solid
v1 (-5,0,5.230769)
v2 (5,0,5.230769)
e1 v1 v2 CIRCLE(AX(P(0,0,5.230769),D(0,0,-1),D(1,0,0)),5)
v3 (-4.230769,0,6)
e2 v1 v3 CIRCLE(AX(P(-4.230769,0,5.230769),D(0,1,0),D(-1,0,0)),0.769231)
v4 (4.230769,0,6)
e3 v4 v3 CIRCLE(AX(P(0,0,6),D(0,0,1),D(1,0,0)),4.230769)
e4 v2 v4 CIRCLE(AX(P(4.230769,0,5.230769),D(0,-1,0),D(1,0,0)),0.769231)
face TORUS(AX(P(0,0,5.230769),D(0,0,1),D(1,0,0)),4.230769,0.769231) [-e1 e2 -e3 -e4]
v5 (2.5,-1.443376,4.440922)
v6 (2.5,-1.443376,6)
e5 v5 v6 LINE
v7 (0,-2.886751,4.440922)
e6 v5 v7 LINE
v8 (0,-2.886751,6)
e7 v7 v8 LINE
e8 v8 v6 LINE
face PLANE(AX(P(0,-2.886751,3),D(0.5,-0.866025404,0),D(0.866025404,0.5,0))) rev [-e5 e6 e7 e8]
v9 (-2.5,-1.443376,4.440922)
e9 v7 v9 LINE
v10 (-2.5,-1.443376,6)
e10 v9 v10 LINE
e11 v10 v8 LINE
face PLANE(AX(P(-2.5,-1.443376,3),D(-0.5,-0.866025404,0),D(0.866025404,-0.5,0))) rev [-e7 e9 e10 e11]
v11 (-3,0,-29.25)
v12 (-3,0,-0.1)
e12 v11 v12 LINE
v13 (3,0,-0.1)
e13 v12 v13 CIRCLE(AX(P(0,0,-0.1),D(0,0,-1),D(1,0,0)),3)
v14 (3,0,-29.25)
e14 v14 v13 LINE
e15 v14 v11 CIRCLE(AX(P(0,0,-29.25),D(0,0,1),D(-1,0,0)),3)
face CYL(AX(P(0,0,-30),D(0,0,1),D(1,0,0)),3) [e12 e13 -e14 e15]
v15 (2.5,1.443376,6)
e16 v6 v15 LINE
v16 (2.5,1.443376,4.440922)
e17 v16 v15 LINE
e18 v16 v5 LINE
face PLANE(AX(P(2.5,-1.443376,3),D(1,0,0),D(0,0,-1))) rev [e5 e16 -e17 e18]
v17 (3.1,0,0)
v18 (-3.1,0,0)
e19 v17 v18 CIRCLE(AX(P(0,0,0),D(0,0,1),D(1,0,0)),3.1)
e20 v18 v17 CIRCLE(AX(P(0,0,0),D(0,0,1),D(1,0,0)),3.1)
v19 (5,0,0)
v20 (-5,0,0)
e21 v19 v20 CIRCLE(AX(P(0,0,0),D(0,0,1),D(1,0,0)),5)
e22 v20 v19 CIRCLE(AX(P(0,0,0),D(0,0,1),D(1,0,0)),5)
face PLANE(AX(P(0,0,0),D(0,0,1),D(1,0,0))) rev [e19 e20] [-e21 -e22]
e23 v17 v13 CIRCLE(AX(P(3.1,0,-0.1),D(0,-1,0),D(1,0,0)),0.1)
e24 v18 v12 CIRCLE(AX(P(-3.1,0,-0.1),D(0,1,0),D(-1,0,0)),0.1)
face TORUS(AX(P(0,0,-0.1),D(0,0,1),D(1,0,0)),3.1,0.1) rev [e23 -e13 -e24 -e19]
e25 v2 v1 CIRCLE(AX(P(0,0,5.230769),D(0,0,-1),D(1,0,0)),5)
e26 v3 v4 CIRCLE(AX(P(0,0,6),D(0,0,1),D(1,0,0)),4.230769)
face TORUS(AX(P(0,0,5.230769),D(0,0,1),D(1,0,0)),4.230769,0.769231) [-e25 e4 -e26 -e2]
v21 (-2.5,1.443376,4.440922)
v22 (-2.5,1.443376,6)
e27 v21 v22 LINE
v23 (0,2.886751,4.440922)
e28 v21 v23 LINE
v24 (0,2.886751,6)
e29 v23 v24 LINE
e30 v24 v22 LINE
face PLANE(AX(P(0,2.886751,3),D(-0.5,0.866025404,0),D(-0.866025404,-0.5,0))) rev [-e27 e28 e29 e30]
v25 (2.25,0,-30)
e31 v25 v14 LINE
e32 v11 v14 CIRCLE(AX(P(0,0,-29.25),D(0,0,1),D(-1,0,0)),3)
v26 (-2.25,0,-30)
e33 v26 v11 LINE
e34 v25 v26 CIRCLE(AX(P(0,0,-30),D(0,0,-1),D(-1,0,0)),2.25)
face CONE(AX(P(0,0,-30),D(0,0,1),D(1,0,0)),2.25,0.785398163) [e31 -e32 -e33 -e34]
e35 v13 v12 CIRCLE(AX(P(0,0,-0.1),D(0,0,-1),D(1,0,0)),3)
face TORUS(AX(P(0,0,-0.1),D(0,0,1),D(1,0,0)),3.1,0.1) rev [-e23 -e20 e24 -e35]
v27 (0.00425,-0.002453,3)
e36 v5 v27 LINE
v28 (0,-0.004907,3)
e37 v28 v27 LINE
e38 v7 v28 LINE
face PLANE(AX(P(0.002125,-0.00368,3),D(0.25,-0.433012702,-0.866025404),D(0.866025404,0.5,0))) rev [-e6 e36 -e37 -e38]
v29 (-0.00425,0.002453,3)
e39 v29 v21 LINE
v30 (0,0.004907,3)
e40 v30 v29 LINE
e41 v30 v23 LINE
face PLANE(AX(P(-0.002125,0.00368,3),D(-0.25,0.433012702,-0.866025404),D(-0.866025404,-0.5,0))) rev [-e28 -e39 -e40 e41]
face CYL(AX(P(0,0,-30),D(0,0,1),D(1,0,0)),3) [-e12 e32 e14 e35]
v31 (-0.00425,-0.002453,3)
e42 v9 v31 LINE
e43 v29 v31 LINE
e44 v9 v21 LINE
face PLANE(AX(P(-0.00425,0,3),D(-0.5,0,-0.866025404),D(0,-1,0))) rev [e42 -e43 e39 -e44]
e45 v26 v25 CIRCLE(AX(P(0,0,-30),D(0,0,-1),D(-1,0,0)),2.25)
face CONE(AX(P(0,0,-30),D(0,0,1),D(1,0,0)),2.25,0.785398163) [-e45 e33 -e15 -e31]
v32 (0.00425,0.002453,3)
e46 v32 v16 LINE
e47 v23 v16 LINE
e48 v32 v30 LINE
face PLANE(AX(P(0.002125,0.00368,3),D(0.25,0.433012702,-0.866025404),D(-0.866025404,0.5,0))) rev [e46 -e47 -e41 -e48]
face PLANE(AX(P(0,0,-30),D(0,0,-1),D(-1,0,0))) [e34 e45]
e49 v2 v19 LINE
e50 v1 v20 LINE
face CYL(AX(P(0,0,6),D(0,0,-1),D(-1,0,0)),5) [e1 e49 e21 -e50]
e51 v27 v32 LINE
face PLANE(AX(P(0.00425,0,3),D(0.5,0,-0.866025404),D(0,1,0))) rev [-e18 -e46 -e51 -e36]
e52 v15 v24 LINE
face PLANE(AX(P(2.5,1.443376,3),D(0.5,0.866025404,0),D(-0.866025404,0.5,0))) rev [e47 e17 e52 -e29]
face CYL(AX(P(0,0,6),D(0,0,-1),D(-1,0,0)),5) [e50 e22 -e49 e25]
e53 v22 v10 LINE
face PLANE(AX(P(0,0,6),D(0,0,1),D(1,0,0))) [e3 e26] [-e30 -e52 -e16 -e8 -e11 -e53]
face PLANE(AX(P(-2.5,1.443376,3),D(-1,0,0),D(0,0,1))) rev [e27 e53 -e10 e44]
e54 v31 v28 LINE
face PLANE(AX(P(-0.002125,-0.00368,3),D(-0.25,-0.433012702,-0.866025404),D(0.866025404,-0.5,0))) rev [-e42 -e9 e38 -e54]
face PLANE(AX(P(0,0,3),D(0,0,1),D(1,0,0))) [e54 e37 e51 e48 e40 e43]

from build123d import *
from OCP.BRepFilletAPI import BRepFilletAPI_MakeChamfer

# Parameters (mm, degrees)
SKETCH1_R           = 5
BOSS_EXTRUDE1_DEPTH = 6
CUT_EXTRUDE1_DEPTH  = 3
SKETCH3_R           = 3
BOSS_EXTRUDE2_DEPTH = 30
CHAMFER1_SIZE       = 0.75
FILLET1_R           = 0.769230769
CHAMFER2_SIZE       = 1.44092219
CHAMFER2_SIZE2      = 2.495750443
FILLET2_R           = 0.1


with BuildPart() as part:
    # Sketch1 → Boss-Extrude1 (new body)
    with BuildSketch(Plane.XY):
        Circle(SKETCH1_R)
    extrude(amount=BOSS_EXTRUDE1_DEPTH)

    # Sketch2 → Cut-Extrude1 (cut)
    with BuildSketch(Plane.XY.offset(6)):
        Polygon((2.5, 1.443375673), (0, 2.886751346), (-2.5, 1.443375673), (-2.5, -1.443375673), (0, -2.886751346), (2.5, -1.443375673), align=None)
    extrude(amount=-CUT_EXTRUDE1_DEPTH, mode=Mode.SUBTRACT)

    # Sketch3 → Boss-Extrude2 (add)
    with BuildSketch(Plane(origin=(0, 0, 0), x_dir=(-1, 0, 0), z_dir=(0, 0, -1))):
        with Locations(Location((0, 0, 0), (0, 0, 180))):
            Circle(SKETCH3_R)
    extrude(amount=BOSS_EXTRUDE2_DEPTH)

    # Chamfer1
    chamfer1_edges = [part.edges().sort_by_distance(p)[0] for p in [
        (-3, 0, -30),
    ]]
    chamfer(chamfer1_edges, length=CHAMFER1_SIZE)

    # Fillet1
    fillet1_edges = [part.edges().sort_by_distance(p)[0] for p in [
        (-5, 0, 6),
    ]]
    fillet(fillet1_edges, radius=FILLET1_R)

    # Chamfer2: one chamfer whose edges measure the first distance from different faces: ONE call of the kernel's chamfer builder (chamfer() names one face for all edges)
    chamfer2_edges_1 = [part.edges().sort_by_distance(p)[0] for p in [
        (-1.25, 2.165063509, 3),
    ]]
    chamfer2_side_1 = [part.faces().sort_by_distance(p)[0] for p in [
        (-1.25, 2.165063509, 4.5),
    ]]
    chamfer2_edges_2 = [part.edges().sort_by_distance(p)[0] for p in [
        (1.25, 2.165063509, 3),
    ]]
    chamfer2_side_2 = [part.faces().sort_by_distance(p)[0] for p in [
        (1.25, 2.165063509, 4.5),
    ]]
    chamfer2_edges_3 = [part.edges().sort_by_distance(p)[0] for p in [
        (2.5, 0, 3),
    ]]
    chamfer2_side_3 = [part.faces().sort_by_distance(p)[0] for p in [
        (2.5, 0, 4.5),
    ]]
    chamfer2_edges_4 = [part.edges().sort_by_distance(p)[0] for p in [
        (1.25, -2.165063509, 3),
    ]]
    chamfer2_side_4 = [part.faces().sort_by_distance(p)[0] for p in [
        (1.25, -2.165063509, 4.5),
    ]]
    chamfer2_edges_5 = [part.edges().sort_by_distance(p)[0] for p in [
        (-1.25, -2.165063509, 3),
    ]]
    chamfer2_side_5 = [part.faces().sort_by_distance(p)[0] for p in [
        (-1.25, -2.165063509, 4.5),
    ]]
    chamfer2_edges_6 = [part.edges().sort_by_distance(p)[0] for p in [
        (-2.5, 0, 3),
    ]]
    chamfer2_side_6 = [part.faces().sort_by_distance(p)[0] for p in [
        (-2.5, 0, 4.5),
    ]]
    chamfer2 = BRepFilletAPI_MakeChamfer(part.part.solid().wrapped)
    for e in chamfer2_edges_1:
        chamfer2.Add(CHAMFER2_SIZE, CHAMFER2_SIZE2, e.wrapped, chamfer2_side_1[0].wrapped)  # the first distance lies on this face
    for e in chamfer2_edges_2:
        chamfer2.Add(CHAMFER2_SIZE, CHAMFER2_SIZE2, e.wrapped, chamfer2_side_2[0].wrapped)  # the first distance lies on this face
    for e in chamfer2_edges_3:
        chamfer2.Add(CHAMFER2_SIZE, CHAMFER2_SIZE2, e.wrapped, chamfer2_side_3[0].wrapped)  # the first distance lies on this face
    for e in chamfer2_edges_4:
        chamfer2.Add(CHAMFER2_SIZE, CHAMFER2_SIZE2, e.wrapped, chamfer2_side_4[0].wrapped)  # the first distance lies on this face
    for e in chamfer2_edges_5:
        chamfer2.Add(CHAMFER2_SIZE, CHAMFER2_SIZE2, e.wrapped, chamfer2_side_5[0].wrapped)  # the first distance lies on this face
    for e in chamfer2_edges_6:
        chamfer2.Add(CHAMFER2_SIZE, CHAMFER2_SIZE2, e.wrapped, chamfer2_side_6[0].wrapped)  # the first distance lies on this face
    add(Compound.cast(chamfer2.Shape()), mode=Mode.REPLACE)

    # Fillet2
    fillet2_edges = [part.edges().sort_by_distance(p)[0] for p in [
        (-3, 0, 0),
    ]]
    fillet(fillet2_edges, radius=FILLET2_R)


solid = part.part
